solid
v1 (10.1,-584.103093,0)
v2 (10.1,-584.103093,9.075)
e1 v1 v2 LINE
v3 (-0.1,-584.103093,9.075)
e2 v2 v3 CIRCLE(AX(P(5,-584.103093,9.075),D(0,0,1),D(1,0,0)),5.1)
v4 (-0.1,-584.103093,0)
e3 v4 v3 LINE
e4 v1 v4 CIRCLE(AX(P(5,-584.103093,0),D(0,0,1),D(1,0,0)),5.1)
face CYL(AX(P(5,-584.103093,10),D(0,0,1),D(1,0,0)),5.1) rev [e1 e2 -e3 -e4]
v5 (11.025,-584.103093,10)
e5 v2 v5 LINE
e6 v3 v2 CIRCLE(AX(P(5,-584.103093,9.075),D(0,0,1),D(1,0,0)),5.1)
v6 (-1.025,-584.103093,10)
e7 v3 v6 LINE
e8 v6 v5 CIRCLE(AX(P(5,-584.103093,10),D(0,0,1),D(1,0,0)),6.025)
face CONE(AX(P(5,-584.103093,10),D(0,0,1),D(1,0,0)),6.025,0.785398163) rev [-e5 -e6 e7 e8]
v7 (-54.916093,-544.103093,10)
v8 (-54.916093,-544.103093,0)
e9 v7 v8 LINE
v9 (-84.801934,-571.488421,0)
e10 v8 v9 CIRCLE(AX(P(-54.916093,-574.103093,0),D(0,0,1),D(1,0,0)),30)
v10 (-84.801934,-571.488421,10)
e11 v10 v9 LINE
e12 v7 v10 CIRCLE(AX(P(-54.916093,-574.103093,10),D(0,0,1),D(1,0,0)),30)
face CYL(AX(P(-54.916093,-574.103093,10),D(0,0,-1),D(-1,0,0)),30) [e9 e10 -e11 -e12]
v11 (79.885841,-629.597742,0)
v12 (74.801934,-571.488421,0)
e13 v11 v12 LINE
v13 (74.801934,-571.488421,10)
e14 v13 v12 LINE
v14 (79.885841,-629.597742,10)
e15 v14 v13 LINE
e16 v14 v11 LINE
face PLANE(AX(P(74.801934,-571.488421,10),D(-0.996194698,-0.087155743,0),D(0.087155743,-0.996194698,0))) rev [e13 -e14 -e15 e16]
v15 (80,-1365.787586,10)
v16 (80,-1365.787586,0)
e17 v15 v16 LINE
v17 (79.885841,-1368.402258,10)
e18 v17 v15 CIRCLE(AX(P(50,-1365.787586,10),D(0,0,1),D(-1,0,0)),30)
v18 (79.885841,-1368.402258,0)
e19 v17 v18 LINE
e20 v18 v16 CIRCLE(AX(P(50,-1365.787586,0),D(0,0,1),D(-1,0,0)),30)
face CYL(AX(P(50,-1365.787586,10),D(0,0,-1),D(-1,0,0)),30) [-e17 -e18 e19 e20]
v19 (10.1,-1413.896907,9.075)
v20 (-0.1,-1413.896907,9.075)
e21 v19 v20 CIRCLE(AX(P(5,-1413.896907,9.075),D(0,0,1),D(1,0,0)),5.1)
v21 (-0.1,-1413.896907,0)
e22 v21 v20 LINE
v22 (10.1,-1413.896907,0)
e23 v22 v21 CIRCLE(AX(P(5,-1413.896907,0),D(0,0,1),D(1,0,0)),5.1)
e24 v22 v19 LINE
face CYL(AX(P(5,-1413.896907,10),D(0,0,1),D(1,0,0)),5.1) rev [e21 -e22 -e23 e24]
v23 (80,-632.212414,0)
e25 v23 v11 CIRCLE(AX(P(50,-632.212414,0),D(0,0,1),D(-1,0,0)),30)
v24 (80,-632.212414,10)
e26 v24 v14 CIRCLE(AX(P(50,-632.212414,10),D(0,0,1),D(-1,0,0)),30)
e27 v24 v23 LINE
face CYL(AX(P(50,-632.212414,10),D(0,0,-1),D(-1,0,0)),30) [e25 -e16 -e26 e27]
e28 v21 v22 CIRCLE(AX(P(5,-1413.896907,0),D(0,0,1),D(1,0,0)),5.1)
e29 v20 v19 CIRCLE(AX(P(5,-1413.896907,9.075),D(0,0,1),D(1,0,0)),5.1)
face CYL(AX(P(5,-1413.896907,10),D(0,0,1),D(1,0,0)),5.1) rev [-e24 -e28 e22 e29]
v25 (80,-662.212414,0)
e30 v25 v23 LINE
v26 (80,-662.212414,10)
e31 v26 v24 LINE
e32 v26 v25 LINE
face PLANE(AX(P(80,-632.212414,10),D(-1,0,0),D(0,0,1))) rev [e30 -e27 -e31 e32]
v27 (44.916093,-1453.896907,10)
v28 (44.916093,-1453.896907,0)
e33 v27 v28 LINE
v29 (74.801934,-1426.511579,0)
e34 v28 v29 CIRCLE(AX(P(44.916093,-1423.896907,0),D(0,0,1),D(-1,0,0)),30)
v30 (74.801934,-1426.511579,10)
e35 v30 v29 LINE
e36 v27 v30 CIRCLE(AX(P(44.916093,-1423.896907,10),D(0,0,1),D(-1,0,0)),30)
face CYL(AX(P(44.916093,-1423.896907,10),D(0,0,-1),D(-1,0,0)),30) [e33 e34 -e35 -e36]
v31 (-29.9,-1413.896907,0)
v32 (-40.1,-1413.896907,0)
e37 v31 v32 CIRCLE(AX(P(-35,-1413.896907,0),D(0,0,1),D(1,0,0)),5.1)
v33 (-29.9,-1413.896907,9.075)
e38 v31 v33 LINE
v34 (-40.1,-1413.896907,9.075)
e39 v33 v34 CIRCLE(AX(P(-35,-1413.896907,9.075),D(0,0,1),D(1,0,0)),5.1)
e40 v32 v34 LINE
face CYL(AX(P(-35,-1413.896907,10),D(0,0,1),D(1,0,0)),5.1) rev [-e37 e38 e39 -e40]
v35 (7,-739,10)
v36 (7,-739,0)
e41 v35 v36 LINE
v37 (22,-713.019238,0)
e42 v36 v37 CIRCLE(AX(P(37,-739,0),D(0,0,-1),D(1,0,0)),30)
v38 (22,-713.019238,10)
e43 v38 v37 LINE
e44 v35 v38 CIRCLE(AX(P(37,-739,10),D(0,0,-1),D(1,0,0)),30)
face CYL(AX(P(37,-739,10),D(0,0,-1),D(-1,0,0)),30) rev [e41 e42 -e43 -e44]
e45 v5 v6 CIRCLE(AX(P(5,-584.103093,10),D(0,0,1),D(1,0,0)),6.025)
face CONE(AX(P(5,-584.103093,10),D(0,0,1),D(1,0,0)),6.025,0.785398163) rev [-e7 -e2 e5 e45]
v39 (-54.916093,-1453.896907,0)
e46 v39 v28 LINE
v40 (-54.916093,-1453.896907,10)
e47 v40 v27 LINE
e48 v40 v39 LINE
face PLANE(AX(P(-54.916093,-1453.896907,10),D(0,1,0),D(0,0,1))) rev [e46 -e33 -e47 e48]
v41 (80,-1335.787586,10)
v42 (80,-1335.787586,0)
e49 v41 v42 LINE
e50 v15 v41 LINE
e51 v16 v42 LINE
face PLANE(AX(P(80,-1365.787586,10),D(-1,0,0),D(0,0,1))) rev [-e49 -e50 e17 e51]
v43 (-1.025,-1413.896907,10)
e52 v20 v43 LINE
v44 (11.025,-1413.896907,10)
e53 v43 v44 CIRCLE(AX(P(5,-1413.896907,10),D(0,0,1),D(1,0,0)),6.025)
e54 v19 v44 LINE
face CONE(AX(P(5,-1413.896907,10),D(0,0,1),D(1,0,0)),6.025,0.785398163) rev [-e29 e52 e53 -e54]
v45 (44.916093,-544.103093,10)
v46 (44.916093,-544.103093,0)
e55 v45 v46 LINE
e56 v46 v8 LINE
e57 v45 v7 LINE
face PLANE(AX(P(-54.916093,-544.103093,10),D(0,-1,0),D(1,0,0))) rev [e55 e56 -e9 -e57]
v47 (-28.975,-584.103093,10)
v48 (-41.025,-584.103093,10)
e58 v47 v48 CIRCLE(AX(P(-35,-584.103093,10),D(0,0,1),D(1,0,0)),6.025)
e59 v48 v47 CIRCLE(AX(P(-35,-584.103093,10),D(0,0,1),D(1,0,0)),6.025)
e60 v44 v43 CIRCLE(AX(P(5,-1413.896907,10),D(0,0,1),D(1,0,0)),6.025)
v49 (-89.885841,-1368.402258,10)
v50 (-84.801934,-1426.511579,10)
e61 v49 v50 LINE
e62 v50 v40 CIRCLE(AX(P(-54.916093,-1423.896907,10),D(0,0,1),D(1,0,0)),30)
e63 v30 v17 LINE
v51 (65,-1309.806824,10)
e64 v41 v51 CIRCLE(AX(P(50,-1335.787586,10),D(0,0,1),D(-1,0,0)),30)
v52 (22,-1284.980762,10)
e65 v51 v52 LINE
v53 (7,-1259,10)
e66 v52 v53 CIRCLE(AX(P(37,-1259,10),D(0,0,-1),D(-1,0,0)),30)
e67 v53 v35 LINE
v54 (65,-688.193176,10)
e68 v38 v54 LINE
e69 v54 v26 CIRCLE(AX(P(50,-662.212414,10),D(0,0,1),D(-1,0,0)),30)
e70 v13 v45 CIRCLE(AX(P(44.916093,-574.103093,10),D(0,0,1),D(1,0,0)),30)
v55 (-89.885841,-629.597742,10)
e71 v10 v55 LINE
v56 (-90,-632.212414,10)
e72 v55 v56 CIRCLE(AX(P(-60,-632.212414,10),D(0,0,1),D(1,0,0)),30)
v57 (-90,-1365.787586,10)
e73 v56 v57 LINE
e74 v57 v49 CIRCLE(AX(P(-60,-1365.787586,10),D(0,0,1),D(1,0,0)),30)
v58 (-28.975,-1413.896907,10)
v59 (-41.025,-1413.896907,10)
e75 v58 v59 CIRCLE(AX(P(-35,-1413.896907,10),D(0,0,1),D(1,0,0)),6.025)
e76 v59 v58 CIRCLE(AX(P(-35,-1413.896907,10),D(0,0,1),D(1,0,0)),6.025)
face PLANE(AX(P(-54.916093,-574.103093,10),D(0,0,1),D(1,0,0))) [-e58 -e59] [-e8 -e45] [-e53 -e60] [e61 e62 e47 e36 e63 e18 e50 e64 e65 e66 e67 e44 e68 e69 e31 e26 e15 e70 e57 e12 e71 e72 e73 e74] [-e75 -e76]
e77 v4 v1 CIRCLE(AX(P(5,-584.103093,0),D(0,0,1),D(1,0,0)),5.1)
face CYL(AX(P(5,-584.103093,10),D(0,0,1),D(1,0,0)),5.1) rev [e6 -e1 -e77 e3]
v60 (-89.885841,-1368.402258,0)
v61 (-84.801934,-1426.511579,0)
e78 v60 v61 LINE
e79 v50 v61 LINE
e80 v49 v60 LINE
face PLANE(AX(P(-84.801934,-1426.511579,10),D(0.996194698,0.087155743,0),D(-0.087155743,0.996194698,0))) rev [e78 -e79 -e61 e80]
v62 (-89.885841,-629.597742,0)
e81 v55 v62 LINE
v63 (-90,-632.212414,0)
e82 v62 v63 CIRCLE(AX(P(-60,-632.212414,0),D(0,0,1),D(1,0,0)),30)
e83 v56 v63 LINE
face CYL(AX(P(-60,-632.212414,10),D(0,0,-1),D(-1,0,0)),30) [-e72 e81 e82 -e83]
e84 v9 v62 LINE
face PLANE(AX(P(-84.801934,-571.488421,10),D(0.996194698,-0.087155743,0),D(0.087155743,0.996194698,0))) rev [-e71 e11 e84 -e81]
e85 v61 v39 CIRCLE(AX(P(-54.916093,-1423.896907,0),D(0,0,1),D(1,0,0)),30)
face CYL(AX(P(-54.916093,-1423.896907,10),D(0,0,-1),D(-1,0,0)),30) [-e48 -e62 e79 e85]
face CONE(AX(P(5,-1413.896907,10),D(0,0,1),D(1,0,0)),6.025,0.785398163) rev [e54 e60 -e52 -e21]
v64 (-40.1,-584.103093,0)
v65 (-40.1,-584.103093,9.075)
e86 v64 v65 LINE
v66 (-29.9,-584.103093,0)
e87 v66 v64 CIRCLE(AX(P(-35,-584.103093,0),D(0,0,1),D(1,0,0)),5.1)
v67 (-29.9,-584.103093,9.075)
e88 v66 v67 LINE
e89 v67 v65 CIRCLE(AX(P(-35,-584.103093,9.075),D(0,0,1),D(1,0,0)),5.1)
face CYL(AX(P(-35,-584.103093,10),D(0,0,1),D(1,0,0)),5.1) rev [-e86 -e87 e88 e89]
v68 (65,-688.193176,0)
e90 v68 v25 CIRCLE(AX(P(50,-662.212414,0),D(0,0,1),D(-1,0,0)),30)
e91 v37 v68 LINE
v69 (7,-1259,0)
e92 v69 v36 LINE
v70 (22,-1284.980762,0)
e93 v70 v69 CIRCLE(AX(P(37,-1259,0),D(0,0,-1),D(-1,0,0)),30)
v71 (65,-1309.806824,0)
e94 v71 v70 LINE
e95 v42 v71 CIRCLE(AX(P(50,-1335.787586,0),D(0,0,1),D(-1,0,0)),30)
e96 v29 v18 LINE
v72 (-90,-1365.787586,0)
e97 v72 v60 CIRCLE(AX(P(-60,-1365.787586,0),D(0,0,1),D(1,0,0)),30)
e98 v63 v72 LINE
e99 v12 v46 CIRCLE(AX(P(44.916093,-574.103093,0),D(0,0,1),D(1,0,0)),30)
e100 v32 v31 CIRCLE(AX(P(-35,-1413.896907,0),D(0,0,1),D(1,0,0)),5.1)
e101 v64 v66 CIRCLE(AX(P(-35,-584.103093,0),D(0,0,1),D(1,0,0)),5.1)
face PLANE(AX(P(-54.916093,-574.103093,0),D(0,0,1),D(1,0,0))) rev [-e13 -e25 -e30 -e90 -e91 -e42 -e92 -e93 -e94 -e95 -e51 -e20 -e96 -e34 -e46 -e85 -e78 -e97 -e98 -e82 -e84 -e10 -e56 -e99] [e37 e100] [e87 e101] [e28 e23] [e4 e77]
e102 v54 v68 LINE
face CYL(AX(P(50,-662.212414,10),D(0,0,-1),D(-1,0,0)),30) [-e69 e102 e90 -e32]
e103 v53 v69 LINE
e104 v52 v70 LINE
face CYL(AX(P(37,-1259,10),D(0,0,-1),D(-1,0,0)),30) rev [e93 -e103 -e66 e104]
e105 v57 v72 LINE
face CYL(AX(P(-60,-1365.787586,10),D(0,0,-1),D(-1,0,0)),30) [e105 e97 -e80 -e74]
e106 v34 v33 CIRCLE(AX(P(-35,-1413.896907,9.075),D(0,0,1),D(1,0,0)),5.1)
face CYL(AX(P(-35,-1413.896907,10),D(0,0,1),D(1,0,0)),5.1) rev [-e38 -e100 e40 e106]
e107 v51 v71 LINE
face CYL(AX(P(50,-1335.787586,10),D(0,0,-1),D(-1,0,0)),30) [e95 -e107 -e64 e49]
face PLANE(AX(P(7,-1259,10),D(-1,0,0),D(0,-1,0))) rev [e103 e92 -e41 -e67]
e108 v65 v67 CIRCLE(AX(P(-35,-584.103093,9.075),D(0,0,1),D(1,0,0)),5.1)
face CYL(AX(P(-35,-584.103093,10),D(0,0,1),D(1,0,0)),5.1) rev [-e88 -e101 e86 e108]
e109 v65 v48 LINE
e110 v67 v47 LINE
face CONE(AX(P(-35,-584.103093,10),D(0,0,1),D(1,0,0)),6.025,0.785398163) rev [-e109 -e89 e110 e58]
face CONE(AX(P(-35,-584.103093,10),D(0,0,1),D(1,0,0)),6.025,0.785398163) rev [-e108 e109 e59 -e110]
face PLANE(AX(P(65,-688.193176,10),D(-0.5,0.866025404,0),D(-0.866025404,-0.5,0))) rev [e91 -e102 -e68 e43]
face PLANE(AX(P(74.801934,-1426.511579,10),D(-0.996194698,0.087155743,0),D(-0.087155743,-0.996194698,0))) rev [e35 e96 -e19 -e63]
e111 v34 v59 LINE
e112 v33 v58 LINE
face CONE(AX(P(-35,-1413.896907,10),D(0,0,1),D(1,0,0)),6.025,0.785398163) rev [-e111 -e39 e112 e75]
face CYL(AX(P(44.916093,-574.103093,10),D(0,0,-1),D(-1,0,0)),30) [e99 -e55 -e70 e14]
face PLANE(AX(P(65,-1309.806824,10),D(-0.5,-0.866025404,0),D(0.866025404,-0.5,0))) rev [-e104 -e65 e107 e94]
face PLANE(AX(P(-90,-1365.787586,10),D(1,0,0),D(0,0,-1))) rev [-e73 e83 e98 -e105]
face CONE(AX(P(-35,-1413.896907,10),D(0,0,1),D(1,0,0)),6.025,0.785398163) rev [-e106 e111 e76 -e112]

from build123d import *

# Parameters (mm, degrees)
EXTRUDE_1_DEPTH               = 10
HOLE_WIZARD_M12_1_D           = 10.2
HOLE_WIZARD_M12_1_CSINK_D     = 12.05
HOLE_WIZARD_M12_1_CSINK_ANGLE = 90


with BuildPart() as part:
    # 草图1 → 凸台-拉伸1 (new body)
    with BuildSketch(Plane.XY):
        with BuildLine():
            Line((-84.801934074, -1426.511579499), (-89.885840943, -1368.402258085))
            ThreePointArc((-89.885840943, -1368.402258085), (-89.971446647, -1367.096167423), (-90, -1365.787585802))
            Line((-90, -1365.787585802), (-90, -632.212414198))
            ThreePointArc((-90, -632.212414198), (-89.971446647, -630.903832577), (-89.885840943, -629.597741915))
            Line((-89.885840943, -629.597741915), (-84.801934074, -571.488420501))
            ThreePointArc((-84.801934074, -571.488420501), (-75.18379936, -551.984772679), (-54.916093131, -544.103092784))
            Line((-54.916093131, -544.103092784), (44.916093131, -544.103092784))
            ThreePointArc((44.916093131, -544.103092784), (65.18379936, -551.984772679), (74.801934074, -571.488420501))
            Line((74.801934074, -571.488420501), (79.885840943, -629.597741915))
            ThreePointArc((79.885840943, -629.597741915), (79.971446647, -630.903832577), (80, -632.212414198))
            Line((80, -632.212414198), (80, -662.212414198))
            ThreePointArc((80, -662.212414198), (75.980762114, -677.212414198), (65, -688.193176311))
            Line((65, -688.193176311), (22, -713.019237886))
            ThreePointArc((22, -713.019237886), (11.019237886, -724), (7, -739))
            Line((7, -739), (7, -1259))
            ThreePointArc((7, -1259), (11.019237886, -1274), (22, -1284.980762114))
            Line((22, -1284.980762114), (65, -1309.806823689))
            ThreePointArc((65, -1309.806823689), (75.980762114, -1320.787585802), (80, -1335.787585802))
            Line((80, -1335.787585802), (80, -1365.787585802))
            ThreePointArc((80, -1365.787585802), (79.971446647, -1367.096167423), (79.885840943, -1368.402258085))
            Line((79.885840943, -1368.402258085), (74.801934074, -1426.511579499))
            ThreePointArc((74.801934074, -1426.511579499), (65.18379936, -1446.015227321), (44.916093131, -1453.896907216))
            Line((44.916093131, -1453.896907216), (-54.916093131, -1453.896907216))
            ThreePointArc((-54.916093131, -1453.896907216), (-75.18379936, -1446.015227321), (-84.801934074, -1426.511579499))
        make_face()
    extrude(amount=EXTRUDE_1_DEPTH)

    # M12 螺纹孔1 (through all)
    with Locations(Plane(origin=(5, -1413.896907216, 10), x_dir=(1, 0, 0), z_dir=(0, 0, 1))):
        with Locations((0, 0), (-40, 0), (-40, 829.793814432), (0, 829.793814432)):
            CounterSinkHole(HOLE_WIZARD_M12_1_D / 2, HOLE_WIZARD_M12_1_CSINK_D / 2, counter_sink_angle=HOLE_WIZARD_M12_1_CSINK_ANGLE)


solid = part.part
